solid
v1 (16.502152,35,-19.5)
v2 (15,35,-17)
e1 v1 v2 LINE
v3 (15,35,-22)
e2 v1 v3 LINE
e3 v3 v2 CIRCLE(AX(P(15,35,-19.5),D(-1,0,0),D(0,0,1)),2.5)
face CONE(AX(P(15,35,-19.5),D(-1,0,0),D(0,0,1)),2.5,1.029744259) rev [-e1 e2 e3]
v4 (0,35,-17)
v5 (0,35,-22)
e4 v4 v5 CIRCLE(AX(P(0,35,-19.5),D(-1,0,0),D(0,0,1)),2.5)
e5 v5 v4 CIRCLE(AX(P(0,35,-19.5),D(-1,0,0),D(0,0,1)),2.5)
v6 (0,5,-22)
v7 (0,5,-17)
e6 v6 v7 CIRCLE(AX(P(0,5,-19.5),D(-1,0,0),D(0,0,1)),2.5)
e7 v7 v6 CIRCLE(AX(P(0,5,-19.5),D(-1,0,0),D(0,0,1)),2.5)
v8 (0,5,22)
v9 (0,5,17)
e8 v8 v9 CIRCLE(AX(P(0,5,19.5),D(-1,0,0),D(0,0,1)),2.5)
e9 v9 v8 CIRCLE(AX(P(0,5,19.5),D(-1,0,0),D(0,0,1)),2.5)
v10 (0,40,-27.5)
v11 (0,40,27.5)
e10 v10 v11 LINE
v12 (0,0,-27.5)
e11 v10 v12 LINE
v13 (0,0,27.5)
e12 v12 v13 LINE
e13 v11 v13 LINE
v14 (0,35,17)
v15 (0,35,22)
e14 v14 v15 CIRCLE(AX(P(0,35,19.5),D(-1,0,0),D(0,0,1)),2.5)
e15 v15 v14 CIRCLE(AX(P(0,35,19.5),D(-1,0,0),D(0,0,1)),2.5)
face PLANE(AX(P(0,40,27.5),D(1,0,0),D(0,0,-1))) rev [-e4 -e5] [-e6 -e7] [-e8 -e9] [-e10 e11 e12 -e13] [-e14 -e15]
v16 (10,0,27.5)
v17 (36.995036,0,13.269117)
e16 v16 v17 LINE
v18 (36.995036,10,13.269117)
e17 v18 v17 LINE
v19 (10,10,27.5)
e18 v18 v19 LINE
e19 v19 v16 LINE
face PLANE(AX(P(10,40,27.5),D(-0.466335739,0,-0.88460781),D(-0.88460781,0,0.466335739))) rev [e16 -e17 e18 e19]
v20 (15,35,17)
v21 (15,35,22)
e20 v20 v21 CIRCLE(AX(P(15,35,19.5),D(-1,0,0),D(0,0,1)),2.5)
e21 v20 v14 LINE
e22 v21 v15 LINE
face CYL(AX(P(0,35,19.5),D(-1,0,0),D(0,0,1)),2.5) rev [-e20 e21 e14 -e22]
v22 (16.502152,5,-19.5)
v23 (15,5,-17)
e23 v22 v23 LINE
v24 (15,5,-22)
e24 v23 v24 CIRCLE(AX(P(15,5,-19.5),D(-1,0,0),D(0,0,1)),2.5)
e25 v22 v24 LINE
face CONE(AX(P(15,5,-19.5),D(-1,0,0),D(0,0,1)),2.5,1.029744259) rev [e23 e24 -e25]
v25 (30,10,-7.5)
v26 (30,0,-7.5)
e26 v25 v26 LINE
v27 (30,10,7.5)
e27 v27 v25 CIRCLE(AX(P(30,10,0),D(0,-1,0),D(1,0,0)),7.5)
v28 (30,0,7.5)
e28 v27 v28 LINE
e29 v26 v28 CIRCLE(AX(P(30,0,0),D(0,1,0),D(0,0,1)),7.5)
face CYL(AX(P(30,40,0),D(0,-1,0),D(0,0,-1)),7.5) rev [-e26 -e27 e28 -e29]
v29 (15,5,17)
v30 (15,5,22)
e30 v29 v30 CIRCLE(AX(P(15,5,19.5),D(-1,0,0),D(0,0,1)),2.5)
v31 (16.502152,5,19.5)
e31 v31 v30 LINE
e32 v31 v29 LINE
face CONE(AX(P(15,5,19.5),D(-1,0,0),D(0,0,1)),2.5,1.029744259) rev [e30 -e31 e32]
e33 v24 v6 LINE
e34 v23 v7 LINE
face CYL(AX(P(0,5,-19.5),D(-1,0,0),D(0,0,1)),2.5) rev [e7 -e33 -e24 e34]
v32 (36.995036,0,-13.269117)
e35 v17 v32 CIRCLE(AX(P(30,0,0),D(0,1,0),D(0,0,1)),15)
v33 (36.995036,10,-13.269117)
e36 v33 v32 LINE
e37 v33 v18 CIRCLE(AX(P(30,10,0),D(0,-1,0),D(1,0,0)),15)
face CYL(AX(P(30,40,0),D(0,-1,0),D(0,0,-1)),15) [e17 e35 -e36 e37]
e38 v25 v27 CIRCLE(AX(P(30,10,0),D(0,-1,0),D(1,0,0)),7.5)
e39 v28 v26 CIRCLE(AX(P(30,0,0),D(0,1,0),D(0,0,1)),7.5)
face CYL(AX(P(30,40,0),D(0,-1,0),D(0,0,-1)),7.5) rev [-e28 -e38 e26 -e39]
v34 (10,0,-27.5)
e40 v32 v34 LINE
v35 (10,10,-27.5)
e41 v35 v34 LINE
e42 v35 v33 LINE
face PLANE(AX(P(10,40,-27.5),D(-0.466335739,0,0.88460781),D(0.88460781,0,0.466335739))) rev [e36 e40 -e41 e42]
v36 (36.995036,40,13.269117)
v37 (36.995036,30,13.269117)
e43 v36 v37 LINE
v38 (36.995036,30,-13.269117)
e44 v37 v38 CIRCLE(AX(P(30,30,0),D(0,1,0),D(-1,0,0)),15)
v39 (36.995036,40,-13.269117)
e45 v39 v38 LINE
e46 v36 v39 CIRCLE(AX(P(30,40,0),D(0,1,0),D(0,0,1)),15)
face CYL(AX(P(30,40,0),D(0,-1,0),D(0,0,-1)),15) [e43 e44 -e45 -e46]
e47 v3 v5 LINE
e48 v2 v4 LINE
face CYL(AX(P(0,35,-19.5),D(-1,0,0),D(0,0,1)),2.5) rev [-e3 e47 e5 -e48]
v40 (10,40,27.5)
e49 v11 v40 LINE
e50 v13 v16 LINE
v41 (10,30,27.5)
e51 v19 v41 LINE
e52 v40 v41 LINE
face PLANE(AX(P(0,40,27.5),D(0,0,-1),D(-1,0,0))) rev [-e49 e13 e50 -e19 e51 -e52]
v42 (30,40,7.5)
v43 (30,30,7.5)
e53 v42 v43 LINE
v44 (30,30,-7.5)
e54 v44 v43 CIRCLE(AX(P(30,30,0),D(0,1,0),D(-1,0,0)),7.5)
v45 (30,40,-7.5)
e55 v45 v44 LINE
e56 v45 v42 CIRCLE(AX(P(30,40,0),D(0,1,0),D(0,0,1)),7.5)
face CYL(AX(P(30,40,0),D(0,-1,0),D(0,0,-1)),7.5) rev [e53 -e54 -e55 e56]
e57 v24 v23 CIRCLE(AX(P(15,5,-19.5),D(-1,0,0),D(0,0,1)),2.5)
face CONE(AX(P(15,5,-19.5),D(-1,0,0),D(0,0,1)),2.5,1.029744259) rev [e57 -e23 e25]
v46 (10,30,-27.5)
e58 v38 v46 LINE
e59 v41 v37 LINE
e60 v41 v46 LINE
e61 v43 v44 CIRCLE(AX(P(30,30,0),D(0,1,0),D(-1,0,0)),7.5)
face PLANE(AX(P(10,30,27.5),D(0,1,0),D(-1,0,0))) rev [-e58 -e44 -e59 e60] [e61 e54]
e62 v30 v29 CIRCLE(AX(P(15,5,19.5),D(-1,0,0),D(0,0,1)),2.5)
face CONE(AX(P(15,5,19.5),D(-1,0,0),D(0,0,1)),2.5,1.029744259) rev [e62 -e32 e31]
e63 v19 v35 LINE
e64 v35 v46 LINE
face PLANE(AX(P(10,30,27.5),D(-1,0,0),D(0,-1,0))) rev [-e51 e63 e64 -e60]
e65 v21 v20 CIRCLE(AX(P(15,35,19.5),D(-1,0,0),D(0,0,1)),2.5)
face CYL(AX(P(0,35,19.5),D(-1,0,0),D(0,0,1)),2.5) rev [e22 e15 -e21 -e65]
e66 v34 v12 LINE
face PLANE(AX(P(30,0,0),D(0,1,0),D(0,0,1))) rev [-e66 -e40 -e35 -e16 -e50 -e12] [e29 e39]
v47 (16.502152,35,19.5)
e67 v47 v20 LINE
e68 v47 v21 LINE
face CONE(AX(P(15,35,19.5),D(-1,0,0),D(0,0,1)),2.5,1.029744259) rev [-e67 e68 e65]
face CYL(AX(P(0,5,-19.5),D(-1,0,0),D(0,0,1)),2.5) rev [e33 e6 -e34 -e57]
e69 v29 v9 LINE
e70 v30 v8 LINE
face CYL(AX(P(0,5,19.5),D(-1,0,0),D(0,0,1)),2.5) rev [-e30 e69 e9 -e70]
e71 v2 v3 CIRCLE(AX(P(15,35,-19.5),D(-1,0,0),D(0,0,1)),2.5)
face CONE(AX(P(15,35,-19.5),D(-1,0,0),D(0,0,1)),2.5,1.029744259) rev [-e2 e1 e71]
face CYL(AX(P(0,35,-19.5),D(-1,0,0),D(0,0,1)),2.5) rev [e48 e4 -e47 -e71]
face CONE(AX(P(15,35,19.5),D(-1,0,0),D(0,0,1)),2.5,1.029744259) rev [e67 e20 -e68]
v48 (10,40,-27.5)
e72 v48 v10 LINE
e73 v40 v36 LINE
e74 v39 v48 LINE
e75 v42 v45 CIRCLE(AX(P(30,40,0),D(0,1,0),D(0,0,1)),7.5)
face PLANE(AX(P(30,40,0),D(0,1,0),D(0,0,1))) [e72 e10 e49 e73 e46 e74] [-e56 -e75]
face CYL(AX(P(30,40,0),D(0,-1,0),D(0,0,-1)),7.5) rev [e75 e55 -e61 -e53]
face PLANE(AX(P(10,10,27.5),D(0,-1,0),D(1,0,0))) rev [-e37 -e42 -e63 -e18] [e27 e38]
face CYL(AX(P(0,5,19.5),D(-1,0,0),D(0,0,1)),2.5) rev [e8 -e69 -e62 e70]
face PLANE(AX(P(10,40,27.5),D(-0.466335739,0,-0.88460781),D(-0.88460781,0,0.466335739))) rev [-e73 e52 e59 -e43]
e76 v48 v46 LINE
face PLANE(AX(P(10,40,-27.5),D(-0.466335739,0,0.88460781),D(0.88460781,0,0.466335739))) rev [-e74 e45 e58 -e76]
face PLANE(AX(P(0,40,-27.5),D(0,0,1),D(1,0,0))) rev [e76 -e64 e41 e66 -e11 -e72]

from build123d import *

# Parameters (mm, degrees)
SKETCH_1_R             = 7.5
EXTRUDE_1_DEPTH        = 40
SKETCH_2_W             = 54.950775634
SKETCH_2_H             = 20
CUT_EXTRUDE_1_DEPTH    = 82.547532152
HOLE_WIZARD_M6_1_D     = 5
HOLE_WIZARD_M6_1_DEPTH = 15
HOLE_WIZARD_M6_1_TIP   = 1.502151548


with BuildPart() as part:
    # 草图1 → 凸台-拉伸1 (new body)
    with BuildSketch(Plane(origin=(0, 0, 0), x_dir=(1, 0, 0), z_dir=(0, 1, 0))):
        with BuildLine():
            Line((0, -27.5), (0, 27.5))
            Line((0, 27.5), (10, 27.5))
            Line((10, 27.5), (36.99503609, 13.269117156))
            ThreePointArc((36.99503609, 13.269117156), (45, 0), (36.99503609, -13.269117156))
            Line((36.99503609, -13.269117156), (10, -27.5))
            Line((10, -27.5), (0, -27.5))
        make_face()
        with Locations(Location((30, 0, 0), (0, 0, 270))):
            Circle(SKETCH_1_R, mode=Mode.SUBTRACT)
    extrude(amount=EXTRUDE_1_DEPTH)

    # 草图2 → 切除-拉伸1 (cut, through all)
    with BuildSketch(Plane(origin=(0, 0, -27.5), x_dir=(-1, 0, 0), z_dir=(0, 0, -1))):
        with Locations((-37.475387817, 20)):
            Rectangle(SKETCH_2_W, SKETCH_2_H)
    extrude(amount=-CUT_EXTRUDE_1_DEPTH, mode=Mode.SUBTRACT)

    # M6 螺纹孔1
    with Locations(Plane.ZY):
        with Locations((-19.5, 5), (-19.5, 35), (19.5, 5), (19.5, 35)):
            Hole(HOLE_WIZARD_M6_1_D / 2, depth=HOLE_WIZARD_M6_1_DEPTH)
            with Locations((0, 0, -(HOLE_WIZARD_M6_1_DEPTH + HOLE_WIZARD_M6_1_TIP / 2))):  # 118° drill point
                Cone(0, HOLE_WIZARD_M6_1_D / 2, HOLE_WIZARD_M6_1_TIP, mode=Mode.SUBTRACT)


solid = part.part
